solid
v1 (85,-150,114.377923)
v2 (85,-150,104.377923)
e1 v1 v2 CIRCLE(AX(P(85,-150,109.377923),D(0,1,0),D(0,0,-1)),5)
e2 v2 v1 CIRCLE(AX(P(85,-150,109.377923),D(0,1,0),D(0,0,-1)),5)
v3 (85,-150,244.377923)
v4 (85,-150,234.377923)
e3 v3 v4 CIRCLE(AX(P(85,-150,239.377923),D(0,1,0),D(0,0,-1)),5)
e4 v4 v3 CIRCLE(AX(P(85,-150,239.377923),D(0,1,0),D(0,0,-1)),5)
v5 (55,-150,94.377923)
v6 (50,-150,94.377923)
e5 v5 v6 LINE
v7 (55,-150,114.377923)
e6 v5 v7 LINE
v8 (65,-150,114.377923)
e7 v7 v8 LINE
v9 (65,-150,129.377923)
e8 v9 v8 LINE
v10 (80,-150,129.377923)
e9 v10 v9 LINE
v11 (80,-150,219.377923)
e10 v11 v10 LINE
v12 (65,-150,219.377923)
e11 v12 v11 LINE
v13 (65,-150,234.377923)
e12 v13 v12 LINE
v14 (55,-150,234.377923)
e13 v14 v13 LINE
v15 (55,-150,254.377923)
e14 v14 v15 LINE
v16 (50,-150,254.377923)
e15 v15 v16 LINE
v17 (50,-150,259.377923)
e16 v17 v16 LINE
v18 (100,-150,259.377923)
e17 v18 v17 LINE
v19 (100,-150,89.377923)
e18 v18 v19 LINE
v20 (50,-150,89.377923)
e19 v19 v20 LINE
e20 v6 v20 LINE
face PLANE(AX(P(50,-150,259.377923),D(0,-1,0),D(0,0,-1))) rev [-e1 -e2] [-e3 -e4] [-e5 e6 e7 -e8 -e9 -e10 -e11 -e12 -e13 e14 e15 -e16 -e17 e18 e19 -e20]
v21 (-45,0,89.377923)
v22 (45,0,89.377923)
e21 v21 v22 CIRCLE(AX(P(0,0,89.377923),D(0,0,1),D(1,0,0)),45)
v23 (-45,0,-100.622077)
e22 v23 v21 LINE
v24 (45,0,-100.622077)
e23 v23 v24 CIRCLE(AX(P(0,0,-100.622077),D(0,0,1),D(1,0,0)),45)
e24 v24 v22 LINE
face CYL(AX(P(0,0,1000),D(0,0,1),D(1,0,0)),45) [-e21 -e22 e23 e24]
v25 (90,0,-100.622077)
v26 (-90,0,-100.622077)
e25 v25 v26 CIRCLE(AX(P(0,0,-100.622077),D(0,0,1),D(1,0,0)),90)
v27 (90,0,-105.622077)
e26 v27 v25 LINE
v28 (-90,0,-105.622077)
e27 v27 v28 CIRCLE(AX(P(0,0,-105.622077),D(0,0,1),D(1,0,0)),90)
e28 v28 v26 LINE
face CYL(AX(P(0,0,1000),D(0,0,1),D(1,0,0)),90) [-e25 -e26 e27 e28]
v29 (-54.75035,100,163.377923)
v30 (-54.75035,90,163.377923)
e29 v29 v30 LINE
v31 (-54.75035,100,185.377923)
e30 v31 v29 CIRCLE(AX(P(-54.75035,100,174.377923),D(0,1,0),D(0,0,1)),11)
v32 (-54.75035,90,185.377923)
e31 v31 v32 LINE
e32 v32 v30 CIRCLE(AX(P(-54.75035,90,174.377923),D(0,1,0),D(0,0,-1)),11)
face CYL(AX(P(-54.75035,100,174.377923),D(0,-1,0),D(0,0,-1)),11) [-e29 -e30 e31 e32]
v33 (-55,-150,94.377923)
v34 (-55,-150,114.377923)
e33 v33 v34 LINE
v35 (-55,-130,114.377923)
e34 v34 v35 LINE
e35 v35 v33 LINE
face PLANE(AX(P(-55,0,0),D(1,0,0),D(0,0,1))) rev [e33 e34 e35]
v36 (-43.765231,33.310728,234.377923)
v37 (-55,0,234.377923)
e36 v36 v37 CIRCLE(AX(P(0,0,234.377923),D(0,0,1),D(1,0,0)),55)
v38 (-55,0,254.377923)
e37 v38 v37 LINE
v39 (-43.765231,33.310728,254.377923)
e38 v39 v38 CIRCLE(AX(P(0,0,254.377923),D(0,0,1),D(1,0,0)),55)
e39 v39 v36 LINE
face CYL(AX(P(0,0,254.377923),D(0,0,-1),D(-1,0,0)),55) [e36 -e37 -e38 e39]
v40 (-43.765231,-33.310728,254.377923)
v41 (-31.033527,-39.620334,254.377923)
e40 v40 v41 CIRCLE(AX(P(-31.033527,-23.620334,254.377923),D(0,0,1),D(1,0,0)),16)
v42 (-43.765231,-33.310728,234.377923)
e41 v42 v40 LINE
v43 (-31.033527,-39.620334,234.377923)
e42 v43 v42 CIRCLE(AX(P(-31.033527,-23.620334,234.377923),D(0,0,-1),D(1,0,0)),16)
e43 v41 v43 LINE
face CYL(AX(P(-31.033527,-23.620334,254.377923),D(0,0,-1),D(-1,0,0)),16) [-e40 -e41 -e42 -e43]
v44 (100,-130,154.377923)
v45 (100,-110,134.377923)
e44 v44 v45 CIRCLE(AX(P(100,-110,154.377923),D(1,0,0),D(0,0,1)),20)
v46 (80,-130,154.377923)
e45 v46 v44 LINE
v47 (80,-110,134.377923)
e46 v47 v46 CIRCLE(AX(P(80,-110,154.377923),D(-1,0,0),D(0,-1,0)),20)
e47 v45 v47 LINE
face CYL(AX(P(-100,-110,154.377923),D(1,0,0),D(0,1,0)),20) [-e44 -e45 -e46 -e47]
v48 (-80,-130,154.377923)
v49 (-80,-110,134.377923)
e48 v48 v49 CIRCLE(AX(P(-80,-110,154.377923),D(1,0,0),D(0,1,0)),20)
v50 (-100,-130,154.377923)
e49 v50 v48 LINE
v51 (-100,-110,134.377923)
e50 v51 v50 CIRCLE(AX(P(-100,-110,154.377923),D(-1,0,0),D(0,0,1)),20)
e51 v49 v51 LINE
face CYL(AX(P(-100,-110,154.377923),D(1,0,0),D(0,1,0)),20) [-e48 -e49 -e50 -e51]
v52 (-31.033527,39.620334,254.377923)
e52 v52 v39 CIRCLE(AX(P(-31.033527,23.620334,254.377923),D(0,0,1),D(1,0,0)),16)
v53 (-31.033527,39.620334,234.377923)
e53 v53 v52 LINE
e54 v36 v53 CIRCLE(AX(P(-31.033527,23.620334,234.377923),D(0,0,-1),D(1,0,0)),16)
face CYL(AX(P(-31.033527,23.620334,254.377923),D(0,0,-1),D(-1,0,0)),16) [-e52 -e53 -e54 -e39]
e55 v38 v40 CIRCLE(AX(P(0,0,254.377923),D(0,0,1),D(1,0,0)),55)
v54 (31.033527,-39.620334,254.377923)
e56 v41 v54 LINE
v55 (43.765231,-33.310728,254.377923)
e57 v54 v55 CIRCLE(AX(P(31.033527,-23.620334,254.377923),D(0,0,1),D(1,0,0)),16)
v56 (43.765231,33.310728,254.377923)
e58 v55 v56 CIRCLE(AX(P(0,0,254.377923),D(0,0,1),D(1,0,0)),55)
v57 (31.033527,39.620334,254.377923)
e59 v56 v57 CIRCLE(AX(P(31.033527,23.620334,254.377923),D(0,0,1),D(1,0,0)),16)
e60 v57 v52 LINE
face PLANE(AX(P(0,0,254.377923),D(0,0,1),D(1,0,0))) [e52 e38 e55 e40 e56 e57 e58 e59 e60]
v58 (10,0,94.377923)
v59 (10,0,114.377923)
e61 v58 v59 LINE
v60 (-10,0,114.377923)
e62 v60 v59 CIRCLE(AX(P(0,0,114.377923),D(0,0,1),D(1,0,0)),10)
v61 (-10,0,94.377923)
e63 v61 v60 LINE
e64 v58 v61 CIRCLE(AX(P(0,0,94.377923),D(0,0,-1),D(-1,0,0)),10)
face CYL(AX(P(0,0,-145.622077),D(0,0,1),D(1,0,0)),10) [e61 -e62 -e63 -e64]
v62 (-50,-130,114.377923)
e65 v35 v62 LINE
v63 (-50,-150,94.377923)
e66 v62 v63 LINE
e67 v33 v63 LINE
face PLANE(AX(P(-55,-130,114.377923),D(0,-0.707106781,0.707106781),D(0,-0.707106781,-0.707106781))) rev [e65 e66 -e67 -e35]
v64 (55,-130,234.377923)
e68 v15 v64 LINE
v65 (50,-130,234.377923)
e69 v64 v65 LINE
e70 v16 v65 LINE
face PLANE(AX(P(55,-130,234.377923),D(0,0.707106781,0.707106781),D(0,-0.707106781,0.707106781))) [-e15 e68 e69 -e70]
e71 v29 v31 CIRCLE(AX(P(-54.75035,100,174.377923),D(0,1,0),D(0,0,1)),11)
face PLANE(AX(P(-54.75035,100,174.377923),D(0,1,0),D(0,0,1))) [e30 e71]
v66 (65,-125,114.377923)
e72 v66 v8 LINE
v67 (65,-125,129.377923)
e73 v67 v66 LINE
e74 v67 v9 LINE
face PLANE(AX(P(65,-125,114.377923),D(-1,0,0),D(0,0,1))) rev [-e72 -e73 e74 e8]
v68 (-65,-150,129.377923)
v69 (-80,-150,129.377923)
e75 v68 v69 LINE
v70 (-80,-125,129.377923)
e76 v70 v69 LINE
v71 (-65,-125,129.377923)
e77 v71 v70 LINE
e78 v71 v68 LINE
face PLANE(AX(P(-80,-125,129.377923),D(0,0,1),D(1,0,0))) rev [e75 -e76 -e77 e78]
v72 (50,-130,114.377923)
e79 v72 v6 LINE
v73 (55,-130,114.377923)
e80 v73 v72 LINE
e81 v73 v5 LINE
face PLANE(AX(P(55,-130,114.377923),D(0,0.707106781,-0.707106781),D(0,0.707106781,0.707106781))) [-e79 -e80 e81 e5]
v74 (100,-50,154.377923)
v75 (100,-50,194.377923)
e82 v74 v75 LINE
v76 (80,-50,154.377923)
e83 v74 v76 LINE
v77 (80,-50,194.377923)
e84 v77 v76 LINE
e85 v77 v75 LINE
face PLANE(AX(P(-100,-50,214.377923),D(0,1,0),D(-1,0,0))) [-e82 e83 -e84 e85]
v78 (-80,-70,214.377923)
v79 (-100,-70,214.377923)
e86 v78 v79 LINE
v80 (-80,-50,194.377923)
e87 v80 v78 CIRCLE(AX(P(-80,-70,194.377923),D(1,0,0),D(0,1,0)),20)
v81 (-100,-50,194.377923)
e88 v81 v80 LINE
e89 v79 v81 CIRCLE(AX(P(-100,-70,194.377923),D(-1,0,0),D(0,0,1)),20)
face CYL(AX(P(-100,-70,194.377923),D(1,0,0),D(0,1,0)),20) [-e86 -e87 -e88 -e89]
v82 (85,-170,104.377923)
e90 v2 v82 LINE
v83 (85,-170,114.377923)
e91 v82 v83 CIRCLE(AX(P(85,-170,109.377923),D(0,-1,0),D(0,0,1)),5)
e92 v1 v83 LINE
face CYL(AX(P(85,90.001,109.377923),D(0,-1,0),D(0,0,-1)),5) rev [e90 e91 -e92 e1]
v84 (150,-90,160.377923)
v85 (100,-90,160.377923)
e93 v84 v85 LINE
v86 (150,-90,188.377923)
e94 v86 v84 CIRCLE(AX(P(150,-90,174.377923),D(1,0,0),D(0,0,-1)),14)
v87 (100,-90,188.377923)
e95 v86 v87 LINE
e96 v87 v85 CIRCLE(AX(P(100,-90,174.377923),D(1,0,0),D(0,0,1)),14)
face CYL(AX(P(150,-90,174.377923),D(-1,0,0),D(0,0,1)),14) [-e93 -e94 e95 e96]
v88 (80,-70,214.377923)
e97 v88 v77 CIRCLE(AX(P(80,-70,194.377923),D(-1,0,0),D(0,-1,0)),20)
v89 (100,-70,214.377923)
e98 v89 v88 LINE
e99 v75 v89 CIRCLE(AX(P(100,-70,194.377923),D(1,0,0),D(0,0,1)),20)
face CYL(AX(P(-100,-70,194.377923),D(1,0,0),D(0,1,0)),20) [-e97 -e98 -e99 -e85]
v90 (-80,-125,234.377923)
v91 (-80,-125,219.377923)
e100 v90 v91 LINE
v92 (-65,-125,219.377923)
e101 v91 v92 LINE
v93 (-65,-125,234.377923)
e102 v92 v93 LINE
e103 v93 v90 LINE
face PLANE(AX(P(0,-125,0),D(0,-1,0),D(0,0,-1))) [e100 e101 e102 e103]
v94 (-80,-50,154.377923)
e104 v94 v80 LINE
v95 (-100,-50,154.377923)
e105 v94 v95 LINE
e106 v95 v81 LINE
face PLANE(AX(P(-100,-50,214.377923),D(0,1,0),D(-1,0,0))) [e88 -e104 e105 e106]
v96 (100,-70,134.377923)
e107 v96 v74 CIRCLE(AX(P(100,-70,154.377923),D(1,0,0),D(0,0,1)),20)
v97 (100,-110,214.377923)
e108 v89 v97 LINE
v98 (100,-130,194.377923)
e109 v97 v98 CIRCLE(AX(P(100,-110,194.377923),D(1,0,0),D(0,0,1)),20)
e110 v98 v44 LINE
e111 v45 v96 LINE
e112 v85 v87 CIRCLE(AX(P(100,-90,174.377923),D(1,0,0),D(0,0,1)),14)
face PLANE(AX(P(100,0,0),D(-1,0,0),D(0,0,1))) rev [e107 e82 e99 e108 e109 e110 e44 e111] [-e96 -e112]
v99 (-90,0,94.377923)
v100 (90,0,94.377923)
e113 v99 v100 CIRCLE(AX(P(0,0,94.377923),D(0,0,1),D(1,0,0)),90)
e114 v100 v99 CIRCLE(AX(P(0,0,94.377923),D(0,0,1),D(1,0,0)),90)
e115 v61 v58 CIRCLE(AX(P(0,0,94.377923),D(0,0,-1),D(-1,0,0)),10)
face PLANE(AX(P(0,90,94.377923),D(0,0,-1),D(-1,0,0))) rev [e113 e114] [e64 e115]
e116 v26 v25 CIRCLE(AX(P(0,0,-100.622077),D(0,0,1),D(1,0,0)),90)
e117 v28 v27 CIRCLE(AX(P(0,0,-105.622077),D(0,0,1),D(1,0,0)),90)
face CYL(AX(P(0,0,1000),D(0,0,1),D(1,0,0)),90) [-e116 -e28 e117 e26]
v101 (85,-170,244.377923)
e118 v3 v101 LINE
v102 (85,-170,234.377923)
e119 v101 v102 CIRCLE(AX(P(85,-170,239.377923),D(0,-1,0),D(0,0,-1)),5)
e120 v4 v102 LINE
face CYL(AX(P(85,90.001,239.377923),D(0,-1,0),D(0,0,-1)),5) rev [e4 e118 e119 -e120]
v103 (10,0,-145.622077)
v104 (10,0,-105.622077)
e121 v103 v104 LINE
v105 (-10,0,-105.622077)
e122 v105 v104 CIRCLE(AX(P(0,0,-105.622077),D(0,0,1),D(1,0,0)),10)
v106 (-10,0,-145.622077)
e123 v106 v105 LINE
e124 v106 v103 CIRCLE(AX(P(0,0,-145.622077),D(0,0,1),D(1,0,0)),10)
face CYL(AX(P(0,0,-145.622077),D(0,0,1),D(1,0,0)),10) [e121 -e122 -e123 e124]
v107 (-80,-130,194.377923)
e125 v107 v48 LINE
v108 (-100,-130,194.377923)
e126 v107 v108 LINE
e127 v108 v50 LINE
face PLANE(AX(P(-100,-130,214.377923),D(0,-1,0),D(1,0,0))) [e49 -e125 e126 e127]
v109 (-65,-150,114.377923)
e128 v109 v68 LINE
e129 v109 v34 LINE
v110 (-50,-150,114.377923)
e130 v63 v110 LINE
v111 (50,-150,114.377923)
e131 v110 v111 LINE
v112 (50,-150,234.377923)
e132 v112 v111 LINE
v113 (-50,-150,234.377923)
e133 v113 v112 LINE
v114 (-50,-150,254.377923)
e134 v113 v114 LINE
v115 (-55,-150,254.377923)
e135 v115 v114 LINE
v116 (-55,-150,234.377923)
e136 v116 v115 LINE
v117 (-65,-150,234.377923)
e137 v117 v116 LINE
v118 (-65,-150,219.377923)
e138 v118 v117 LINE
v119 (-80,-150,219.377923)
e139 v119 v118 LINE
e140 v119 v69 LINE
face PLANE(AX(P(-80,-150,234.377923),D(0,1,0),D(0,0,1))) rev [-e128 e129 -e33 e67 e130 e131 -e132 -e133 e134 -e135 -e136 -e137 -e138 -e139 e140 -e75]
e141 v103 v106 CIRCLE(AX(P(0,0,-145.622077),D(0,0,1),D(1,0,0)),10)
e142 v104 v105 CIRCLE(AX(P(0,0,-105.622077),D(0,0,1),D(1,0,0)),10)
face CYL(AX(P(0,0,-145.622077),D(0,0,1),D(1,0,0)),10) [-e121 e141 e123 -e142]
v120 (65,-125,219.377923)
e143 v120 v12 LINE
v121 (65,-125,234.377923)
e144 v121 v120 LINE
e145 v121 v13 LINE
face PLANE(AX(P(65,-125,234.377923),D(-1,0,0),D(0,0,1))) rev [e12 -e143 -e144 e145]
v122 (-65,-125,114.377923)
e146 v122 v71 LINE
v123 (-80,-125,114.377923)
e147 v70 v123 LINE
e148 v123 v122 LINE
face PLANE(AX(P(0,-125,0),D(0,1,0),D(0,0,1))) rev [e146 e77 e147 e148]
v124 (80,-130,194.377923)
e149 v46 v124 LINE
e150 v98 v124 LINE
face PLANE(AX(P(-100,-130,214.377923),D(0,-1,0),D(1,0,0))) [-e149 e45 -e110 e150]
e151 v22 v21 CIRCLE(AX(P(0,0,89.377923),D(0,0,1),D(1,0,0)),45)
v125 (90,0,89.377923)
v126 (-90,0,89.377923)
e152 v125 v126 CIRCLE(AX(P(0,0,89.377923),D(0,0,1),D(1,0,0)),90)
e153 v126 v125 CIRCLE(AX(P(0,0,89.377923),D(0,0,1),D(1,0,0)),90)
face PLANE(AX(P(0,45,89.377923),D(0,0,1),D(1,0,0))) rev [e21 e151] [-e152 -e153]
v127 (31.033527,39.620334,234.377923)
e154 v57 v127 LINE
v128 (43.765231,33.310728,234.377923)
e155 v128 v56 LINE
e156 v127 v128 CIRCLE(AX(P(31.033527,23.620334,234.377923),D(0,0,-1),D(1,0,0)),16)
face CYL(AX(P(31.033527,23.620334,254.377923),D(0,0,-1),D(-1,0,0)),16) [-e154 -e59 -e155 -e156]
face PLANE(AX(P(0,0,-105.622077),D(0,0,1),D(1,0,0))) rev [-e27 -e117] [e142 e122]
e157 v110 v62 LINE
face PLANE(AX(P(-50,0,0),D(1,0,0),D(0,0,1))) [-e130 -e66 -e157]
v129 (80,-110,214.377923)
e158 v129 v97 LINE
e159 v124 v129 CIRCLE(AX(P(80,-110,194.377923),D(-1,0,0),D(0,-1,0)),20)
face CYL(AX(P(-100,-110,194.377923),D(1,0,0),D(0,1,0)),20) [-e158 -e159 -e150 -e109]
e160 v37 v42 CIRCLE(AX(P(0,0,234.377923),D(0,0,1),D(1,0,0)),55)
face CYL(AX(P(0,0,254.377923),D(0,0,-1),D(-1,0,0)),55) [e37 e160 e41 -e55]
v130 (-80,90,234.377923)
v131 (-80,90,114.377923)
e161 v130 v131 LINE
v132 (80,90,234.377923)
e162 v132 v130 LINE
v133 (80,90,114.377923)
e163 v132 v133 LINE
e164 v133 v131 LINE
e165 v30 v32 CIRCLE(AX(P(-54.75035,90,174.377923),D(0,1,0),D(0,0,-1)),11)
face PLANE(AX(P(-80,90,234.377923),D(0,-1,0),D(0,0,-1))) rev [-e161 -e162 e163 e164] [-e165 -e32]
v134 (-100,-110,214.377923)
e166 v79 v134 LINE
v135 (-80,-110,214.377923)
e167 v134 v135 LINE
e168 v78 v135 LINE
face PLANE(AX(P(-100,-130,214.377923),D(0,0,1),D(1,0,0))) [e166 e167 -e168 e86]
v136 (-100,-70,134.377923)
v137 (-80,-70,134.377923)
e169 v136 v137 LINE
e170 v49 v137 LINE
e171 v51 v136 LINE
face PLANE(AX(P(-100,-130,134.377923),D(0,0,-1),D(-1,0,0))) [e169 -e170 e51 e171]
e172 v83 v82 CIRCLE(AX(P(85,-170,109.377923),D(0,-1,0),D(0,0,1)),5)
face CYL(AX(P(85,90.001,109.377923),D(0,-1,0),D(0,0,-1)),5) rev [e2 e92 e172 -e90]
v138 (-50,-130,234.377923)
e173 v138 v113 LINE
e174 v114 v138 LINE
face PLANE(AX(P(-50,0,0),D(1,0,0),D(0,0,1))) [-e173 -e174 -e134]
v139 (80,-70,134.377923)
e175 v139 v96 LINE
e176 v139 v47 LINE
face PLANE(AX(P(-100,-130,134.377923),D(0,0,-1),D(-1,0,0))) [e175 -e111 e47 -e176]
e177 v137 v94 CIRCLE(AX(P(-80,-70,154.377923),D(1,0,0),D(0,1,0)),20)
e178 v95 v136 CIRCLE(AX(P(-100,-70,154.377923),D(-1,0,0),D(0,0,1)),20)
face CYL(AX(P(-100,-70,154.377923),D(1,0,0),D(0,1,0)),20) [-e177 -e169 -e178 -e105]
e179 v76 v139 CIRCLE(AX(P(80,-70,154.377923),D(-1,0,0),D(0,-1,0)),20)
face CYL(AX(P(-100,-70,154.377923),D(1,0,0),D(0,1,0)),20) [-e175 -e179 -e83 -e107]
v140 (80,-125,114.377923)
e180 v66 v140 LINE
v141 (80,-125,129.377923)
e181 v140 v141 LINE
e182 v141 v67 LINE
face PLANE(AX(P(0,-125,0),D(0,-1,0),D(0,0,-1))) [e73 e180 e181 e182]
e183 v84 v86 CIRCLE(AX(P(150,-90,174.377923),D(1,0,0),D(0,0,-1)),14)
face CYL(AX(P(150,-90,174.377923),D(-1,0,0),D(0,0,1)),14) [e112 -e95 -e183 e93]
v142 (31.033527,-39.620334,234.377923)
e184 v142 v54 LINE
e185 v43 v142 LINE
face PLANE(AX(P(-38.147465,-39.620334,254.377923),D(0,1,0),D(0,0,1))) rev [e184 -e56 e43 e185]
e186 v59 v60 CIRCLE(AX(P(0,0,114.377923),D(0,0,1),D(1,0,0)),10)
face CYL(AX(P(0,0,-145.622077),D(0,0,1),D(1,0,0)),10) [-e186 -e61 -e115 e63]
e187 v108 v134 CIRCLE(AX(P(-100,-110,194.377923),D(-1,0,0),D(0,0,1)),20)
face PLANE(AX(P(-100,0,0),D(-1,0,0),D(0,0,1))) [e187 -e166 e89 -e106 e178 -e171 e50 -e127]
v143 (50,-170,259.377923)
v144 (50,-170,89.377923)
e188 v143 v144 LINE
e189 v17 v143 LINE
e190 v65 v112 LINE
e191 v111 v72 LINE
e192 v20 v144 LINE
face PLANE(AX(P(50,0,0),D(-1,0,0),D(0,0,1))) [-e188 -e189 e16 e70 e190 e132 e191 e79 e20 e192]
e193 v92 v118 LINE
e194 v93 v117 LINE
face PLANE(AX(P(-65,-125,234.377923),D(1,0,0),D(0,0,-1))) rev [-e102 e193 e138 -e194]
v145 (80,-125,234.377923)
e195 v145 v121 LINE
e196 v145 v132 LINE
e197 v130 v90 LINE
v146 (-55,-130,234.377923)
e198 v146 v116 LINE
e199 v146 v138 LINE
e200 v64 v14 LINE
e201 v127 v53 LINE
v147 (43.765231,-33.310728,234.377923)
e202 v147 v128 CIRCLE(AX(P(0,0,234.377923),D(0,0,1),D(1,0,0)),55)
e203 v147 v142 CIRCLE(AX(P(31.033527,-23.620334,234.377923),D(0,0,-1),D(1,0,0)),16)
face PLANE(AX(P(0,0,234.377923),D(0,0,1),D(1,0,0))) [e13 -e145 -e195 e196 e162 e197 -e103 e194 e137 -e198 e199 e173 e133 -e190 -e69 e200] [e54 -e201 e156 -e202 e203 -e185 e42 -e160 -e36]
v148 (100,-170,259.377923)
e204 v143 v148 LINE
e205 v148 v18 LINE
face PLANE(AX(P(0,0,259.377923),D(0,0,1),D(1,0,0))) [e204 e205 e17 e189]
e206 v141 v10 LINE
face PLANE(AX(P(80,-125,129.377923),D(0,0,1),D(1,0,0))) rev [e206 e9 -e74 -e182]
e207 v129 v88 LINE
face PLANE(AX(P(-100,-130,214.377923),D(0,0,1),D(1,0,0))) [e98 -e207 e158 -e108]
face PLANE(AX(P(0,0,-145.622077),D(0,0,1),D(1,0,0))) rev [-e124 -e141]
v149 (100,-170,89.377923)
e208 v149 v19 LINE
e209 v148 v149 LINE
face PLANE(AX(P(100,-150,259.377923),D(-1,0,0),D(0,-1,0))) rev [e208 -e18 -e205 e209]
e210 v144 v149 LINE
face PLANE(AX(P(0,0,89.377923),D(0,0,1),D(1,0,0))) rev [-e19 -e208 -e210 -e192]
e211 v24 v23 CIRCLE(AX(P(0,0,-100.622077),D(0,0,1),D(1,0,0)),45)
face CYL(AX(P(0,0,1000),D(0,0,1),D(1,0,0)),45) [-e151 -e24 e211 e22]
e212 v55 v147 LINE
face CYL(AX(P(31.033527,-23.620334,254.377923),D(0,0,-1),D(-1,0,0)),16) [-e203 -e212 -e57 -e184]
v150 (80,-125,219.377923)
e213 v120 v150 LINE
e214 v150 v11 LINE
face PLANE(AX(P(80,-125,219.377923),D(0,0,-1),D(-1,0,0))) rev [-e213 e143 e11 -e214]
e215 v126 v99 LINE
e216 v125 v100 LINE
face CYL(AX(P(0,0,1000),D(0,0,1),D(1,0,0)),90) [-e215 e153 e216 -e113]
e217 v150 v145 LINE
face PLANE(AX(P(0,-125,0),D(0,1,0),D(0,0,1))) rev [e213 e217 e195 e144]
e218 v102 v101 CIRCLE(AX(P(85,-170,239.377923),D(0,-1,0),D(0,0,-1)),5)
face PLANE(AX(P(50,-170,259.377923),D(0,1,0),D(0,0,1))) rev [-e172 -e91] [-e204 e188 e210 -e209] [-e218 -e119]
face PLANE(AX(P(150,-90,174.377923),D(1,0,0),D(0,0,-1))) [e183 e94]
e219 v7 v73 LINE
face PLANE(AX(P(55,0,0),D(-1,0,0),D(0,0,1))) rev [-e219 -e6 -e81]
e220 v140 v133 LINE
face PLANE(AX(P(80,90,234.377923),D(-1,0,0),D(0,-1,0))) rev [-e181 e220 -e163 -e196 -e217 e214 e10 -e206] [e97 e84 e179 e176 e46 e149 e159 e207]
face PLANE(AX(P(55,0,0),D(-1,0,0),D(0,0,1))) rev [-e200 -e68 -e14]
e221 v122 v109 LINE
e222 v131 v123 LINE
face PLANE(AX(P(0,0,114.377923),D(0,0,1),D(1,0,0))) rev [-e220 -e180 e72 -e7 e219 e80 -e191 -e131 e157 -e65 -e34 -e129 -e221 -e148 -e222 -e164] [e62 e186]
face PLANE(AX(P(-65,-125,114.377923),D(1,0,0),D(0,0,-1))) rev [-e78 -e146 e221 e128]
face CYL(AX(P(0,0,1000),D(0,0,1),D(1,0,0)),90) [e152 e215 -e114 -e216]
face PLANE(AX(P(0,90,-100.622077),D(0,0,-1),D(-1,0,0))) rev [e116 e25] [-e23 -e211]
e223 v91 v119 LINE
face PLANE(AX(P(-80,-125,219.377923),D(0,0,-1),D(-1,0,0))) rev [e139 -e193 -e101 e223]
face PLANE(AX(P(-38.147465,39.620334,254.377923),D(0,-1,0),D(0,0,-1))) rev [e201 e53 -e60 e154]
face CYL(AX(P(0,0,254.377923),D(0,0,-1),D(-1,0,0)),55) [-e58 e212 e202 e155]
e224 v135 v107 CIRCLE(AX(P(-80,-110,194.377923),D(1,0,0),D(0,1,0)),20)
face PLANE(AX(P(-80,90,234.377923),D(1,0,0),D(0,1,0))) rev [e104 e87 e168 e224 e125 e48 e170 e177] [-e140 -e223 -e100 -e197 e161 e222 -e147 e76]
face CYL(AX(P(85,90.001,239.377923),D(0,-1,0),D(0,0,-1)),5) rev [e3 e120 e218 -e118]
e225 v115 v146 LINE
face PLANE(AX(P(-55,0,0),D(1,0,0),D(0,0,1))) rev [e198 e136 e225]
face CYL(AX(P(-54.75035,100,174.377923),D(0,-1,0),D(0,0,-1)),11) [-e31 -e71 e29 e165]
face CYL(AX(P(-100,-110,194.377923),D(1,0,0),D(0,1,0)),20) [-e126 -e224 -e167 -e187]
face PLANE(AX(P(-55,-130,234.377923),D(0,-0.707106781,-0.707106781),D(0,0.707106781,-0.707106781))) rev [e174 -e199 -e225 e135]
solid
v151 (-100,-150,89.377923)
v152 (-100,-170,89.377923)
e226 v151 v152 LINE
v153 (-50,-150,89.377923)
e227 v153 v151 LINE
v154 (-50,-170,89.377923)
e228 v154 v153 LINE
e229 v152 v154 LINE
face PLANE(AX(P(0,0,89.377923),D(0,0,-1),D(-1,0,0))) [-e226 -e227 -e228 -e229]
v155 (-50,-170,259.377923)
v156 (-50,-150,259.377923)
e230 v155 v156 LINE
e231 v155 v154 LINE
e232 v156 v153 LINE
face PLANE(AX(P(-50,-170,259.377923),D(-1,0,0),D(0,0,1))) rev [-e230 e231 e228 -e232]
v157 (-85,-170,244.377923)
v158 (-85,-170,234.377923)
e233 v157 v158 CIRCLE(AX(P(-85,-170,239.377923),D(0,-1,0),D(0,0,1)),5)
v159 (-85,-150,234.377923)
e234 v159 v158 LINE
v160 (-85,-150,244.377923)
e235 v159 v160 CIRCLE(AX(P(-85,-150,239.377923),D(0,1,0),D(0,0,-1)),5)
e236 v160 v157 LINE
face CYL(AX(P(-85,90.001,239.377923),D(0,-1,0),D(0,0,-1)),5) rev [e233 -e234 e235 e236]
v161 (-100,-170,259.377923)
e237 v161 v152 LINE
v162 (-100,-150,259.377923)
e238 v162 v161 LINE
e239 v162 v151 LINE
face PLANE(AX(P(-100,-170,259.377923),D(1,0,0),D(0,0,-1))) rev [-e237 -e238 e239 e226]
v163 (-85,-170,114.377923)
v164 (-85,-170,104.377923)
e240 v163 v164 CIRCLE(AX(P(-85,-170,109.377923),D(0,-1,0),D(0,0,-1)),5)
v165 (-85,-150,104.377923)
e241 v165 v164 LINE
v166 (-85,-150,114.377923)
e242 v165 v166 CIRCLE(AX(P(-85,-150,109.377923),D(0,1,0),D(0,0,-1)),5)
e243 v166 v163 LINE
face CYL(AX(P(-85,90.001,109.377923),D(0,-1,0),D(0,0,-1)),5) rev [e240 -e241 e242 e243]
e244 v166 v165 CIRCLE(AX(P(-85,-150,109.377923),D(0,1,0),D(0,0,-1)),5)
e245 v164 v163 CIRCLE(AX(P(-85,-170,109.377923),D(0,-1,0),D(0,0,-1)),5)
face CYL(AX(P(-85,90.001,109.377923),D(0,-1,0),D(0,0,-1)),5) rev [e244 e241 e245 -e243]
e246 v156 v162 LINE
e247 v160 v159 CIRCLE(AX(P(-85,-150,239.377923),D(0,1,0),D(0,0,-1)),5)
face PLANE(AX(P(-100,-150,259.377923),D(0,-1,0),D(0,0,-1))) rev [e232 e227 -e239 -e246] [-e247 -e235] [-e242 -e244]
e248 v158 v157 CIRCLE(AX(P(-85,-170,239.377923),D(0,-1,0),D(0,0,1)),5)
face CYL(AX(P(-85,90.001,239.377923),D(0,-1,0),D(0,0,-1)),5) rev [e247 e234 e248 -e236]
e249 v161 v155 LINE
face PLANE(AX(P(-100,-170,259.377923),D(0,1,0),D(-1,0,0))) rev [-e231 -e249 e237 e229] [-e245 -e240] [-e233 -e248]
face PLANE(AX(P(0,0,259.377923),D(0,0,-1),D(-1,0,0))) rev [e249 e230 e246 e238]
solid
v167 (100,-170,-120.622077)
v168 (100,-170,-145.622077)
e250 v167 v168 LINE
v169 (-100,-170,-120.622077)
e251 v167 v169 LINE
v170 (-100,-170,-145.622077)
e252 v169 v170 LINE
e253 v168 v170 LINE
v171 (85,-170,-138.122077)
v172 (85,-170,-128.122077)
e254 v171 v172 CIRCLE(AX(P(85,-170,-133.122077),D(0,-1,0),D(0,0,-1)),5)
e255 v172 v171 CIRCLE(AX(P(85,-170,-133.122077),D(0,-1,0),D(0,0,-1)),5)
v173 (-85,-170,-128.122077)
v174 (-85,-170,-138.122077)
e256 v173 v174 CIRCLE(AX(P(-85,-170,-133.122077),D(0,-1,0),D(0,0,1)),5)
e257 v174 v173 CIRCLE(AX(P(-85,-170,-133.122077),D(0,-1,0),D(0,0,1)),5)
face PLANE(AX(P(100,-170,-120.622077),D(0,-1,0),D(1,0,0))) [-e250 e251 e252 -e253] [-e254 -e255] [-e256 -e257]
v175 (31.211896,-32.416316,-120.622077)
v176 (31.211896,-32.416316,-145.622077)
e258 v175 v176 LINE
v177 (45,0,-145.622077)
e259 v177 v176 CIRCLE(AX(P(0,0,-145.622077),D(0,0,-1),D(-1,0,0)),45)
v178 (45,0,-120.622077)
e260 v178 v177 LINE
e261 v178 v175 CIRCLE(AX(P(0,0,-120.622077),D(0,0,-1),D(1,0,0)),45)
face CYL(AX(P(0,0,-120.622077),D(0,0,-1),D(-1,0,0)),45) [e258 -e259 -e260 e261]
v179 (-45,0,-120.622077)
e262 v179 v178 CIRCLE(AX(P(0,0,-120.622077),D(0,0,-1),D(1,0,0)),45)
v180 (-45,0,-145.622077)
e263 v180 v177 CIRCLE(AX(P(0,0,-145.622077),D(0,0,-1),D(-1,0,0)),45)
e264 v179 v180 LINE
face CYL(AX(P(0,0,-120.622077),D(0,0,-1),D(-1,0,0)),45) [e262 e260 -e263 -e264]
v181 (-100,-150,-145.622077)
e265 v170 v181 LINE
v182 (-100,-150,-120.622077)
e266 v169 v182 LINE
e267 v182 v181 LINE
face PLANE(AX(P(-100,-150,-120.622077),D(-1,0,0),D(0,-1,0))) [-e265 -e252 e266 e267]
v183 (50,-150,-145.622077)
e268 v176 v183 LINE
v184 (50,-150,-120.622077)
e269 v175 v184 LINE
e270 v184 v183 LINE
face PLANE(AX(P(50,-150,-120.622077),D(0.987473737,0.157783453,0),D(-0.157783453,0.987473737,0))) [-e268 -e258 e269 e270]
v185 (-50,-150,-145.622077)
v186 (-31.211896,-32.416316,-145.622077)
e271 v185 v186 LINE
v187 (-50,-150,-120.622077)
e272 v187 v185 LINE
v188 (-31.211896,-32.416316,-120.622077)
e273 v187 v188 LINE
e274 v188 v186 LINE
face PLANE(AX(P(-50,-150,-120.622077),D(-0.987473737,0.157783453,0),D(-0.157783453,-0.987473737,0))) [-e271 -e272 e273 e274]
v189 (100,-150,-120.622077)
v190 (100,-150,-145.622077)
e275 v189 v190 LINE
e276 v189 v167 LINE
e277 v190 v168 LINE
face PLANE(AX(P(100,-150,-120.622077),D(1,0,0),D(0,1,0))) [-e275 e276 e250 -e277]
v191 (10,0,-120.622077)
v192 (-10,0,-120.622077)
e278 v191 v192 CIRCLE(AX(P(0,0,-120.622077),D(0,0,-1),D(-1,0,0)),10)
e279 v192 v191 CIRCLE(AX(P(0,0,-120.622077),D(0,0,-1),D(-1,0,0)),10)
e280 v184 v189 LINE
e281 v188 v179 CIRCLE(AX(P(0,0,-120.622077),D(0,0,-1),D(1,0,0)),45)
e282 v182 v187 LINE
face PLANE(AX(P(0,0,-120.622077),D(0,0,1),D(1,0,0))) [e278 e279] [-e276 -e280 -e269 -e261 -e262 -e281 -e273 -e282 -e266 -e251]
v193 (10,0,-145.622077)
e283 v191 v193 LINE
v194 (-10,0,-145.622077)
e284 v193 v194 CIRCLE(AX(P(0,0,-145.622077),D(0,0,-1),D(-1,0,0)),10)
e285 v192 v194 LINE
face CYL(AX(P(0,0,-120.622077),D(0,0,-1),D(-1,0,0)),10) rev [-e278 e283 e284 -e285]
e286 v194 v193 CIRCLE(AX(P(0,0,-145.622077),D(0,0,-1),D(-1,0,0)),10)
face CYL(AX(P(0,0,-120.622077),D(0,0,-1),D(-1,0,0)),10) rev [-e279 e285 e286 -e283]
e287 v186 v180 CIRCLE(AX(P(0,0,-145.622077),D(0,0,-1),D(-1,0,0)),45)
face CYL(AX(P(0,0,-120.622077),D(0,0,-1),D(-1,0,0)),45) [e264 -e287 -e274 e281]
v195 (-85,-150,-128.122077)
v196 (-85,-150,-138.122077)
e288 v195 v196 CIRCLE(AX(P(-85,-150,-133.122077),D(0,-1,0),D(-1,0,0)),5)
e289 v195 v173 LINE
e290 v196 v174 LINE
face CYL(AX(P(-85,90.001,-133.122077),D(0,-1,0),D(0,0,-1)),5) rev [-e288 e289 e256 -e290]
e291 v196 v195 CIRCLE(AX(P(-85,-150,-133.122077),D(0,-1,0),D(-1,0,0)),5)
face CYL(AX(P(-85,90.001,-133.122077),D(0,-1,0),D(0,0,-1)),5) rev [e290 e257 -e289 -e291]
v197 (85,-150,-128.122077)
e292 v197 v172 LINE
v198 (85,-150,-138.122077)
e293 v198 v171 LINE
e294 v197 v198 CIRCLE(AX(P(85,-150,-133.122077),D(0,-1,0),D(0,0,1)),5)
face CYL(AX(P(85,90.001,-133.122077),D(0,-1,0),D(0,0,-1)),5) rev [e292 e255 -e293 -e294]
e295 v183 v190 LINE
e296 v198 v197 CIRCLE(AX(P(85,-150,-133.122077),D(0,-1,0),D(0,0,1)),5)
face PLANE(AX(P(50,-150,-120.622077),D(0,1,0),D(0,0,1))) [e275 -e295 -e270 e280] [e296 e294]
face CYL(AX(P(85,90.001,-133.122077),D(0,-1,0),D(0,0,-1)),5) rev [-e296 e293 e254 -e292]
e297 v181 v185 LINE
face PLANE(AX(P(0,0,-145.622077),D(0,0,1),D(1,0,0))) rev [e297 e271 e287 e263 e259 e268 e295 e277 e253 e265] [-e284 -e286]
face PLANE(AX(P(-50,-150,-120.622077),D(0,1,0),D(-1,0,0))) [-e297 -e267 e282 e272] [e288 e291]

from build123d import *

# Parameters (mm, degrees)
EXTRUDE_1_DEPTH      = 20
EXTRUDE_1_DEPTH_BACK = 240
SKETCH_2_R           = 10
SKETCH_3_W           = 160
SKETCH_3_H           = 240
EXTRUDE_2_DEPTH      = 120
SKETCH_4_R           = 10
EXTRUDE_3_DEPTH      = 25
EXTRUDE_4_DEPTH      = 20
EXTRUDE_5_DEPTH      = 20
EXTRUDE_5_DEPTH_BACK = 180
SKETCH_7_W           = 80
SKETCH_7_H           = 80
FILLET_1_R           = 20
FILLET_2_R           = 16
SKETCH_8_R           = 14
EXTRUDE_6_DEPTH      = 50
SKETCH_10_W          = 50
SKETCH_10_H          = 20
EXTRUDE_7_DEPTH      = 85
EXTRUDE_7_2_DEPTH    = 85
EXTRUDE_8_DEPTH      = 5
SKETCH_12_R          = 5
CUT_EXTRUDE_1_DEPTH  = 20
SKETCH_13_W          = 15
SKETCH_13_H          = 15
CUT_EXTRUDE_2_DEPTH  = 25
SKETCH_14_R          = 11
EXTRUDE_9_DEPTH      = 10


with BuildPart() as part:
    # 草图1 → 旋转1 (revolve)
    with BuildSketch(Plane(origin=(0, 0, 0), x_dir=(0, 0, -1), z_dir=(1, 0, 0)), mode=Mode.PRIVATE) as revolve_1_sk:
        Polygon((-92.42282507, 0), (105.622076707, 0), (105.622076707, 90), (100.622076707, 90), (100.622076707, 45), (-89.377923293, 45), (-89.377923293, 90), (-94.377923293, 90), (-94.377923293, 0), align=None)
    revolve(revolve_1_sk.sketch.rotate(Axis((0, 0, 1000), (0, 0, -1)), 90), axis=Axis((0, 0, 1000), (0, 0, -1)))

    # 草图2 → 凸台-拉伸1 (add, two sides: drawn at the far end of the back side and taken through both)
    with BuildSketch(Plane.XY.offset(94.377923293).offset(-EXTRUDE_1_DEPTH_BACK)):
        Circle(SKETCH_2_R)
    extrude(amount=EXTRUDE_1_DEPTH + EXTRUDE_1_DEPTH_BACK)

    # 草图3 → 凸台-拉伸2 (add)
    with BuildSketch(Plane.XY.offset(114.377923293)):
        with Locations((0, -30)):
            Rectangle(SKETCH_3_W, SKETCH_3_H)
    extrude(amount=EXTRUDE_2_DEPTH)

    # 草图6 → 凸台-拉伸4 (add)
    with BuildSketch(Plane.XY.offset(234.377923293)):
        with BuildLine():
            Line((-38.147465423, 39.620334196), (38.147465423, 39.620334196))
            ThreePointArc((38.147465423, 39.620334196), (55, 0), (38.147465423, -39.620334196))
            Line((38.147465423, -39.620334196), (-38.147465423, -39.620334196))
            ThreePointArc((-38.147465423, -39.620334196), (-55, 0), (-38.147465423, 39.620334196))
        make_face()
    extrude(amount=EXTRUDE_4_DEPTH)

    # 草图7 → 凸台-拉伸5 (add, two sides: drawn at the far end of the back side and taken through both)
    with BuildSketch(Plane(origin=(80, 0, 0), x_dir=(0, 0, -1), z_dir=(1, 0, 0)).offset(-EXTRUDE_5_DEPTH_BACK)):
        with Locations((-174.377923293, -90)):
            Rectangle(SKETCH_7_W, SKETCH_7_H)
    extrude(amount=EXTRUDE_5_DEPTH + EXTRUDE_5_DEPTH_BACK)

    # 圆角1
    fillet_1_edges = [part.edges().sort_by_distance(p)[0] for p in [
        (90, -50, 134.377923293),
        (-90, -50, 134.377923293),
        (90, -130, 134.377923293),
        (-90, -130, 134.377923293),
        (90, -130, 214.377923293),
        (-90, -130, 214.377923293),
        (90, -50, 214.377923293),
        (-90, -50, 214.377923293),
    ]]
    fillet(fillet_1_edges, radius=FILLET_1_R)

    # 圆角2
    fillet_2_edges = [part.edges().sort_by_distance(p)[0] for p in [
        (-38.147465423, 39.620334196, 244.377923293),
        (-38.147465423, -39.620334196, 244.377923293),
        (38.147465423, -39.620334196, 244.377923293),
        (38.147465423, 39.620334196, 244.377923293),
    ]]
    fillet(fillet_2_edges, radius=FILLET_2_R)

    # 草图8 → 凸台-拉伸6 (add)
    with BuildSketch(Plane(origin=(100, 0, 0), x_dir=(0, 0, -1), z_dir=(1, 0, 0))):
        with Locations(Location((-174.377923293, -90, 0), (0, 0, 180))):
            Circle(SKETCH_8_R)
    extrude(amount=EXTRUDE_6_DEPTH)



with BuildPart() as body_2:
    # 草图4 → 凸台-拉伸3 (new body)
    with BuildSketch(Plane(origin=(0, 0, -145.622076707), x_dir=(-1, 0, 0), z_dir=(0, 0, -1))):
        with BuildLine():
            Line((-50, -150), (-100, -150))
            Line((-100, -150), (-100, -170))
            Line((-100, -170), (100, -170))
            Line((100, -170), (100, -150))
            Line((100, -150), (50, -150))
            Line((50, -150), (31.211895674, -32.416316392))
            ThreePointArc((31.211895674, -32.416316392), (41.40975311, -17.613413847), (45, 0))
            ThreePointArc((45, 0), (0, 45), (-45, 0))
            ThreePointArc((-45, 0), (-41.40975311, -17.613413847), (-31.211895674, -32.416316392))
            Line((-31.211895674, -32.416316392), (-50, -150))
        make_face()
        Circle(SKETCH_4_R, mode=Mode.SUBTRACT)
    extrude(amount=-EXTRUDE_3_DEPTH)


with BuildPart() as body_3:
    # 草图10 → 凸台-拉伸7 (new, symmetric)
    with BuildSketch(Plane.XY.offset(174.377923293)):
        with Locations((75, -160)):
            Rectangle(SKETCH_10_W, SKETCH_10_H)
    extrude(amount=EXTRUDE_7_DEPTH, both=True)


with BuildPart() as body_4:
    # 草图10 → Extrude 7 2 (new, symmetric)
    with BuildSketch(Plane.XY.offset(174.377923293)):
        with Locations((-75, -160)):
            Rectangle(SKETCH_10_W, SKETCH_10_H)
    extrude(amount=EXTRUDE_7_2_DEPTH, both=True)


with BuildPart() as part_1:
    add(part.part)

    add(body_3.part)  # 凸台-拉伸8 merges body 3
    # 草图11 → 凸台-拉伸8 (add)
    with BuildSketch(Plane.ZY.offset(-50)):
        Polygon((114.377923293, -130), (94.377923293, -150), (114.377923293, -150), align=None)
        Polygon((234.377923293, -130), (234.377923293, -150), (254.377923293, -150), align=None)
    extrude_8 = extrude(amount=-EXTRUDE_8_DEPTH)

    # 镜向1: 凸台-拉伸8 across plane
    add(extrude_8.mirror(Plane(origin=(0, 0, 0), x_dir=(0, 0, 1), z_dir=(1, 0, 0))))


with BuildPart() as cut_extrude_1_tool:
    # 草图12 → 切除-拉伸1 (new body)
    with BuildSketch(Plane.XZ.offset(170)):
        with Locations(Location((85, 239.377923293, 0), (0, 0, 270))):
            Circle(SKETCH_12_R)
        with Locations(Location((85, 109.377923293, 0), (0, 0, 270))):
            Circle(SKETCH_12_R)
        with Locations(Location((85, -133.122076707, 0), (0, 0, 270))):
            Circle(SKETCH_12_R)
        with Locations(Location((-85, -133.122076707, 0), (0, 0, 180))):
            Circle(SKETCH_12_R)
        with Locations(Location((-85, 109.377923293, 0), (0, 0, 270))):
            Circle(SKETCH_12_R)
        with Locations(Location((-85, 239.377923293, 0), (0, 0, 270))):
            Circle(SKETCH_12_R)
    extrude(amount=-CUT_EXTRUDE_1_DEPTH)


with BuildPart() as part_2:
    add(part_1.part)

    # 切除-拉伸1: cut by cut_extrude_1_tool
    add(cut_extrude_1_tool.part, mode=Mode.SUBTRACT)

    # 草图13 → 切除-拉伸2 (cut)
    with BuildSketch(Plane.XZ.offset(150)):
        with Locations((-72.5, 226.877923293)):
            Rectangle(SKETCH_13_W, SKETCH_13_H)
        with Locations((72.5, 226.877923293)):
            Rectangle(SKETCH_13_W, SKETCH_13_H)
        with Locations((72.5, 121.877923293)):
            Rectangle(SKETCH_13_W, SKETCH_13_H)
        with Locations((-72.5, 121.877923293)):
            Rectangle(SKETCH_13_W, SKETCH_13_H)
    extrude(amount=-CUT_EXTRUDE_2_DEPTH, mode=Mode.SUBTRACT)

    # 草图14 → 凸台-拉伸9 (add)
    with BuildSketch(Plane(origin=(0, 90, 0), x_dir=(1, 0, 0), z_dir=(0, 1, 0))):
        with Locations(Location((-54.750350248, -174.377923293, 0), (0, 0, 90))):
            Circle(SKETCH_14_R)
    extrude(amount=EXTRUDE_9_DEPTH)


with BuildPart() as body_2_1:
    add(body_2.part)

    # 切除-拉伸1: cut by cut_extrude_1_tool
    add(cut_extrude_1_tool.part, mode=Mode.SUBTRACT)


with BuildPart() as body_4_1:
    add(body_4.part)

    # 切除-拉伸1: cut by cut_extrude_1_tool
    add(cut_extrude_1_tool.part, mode=Mode.SUBTRACT)


solid = Compound([part_2.part, body_2_1.part, body_4_1.part])
